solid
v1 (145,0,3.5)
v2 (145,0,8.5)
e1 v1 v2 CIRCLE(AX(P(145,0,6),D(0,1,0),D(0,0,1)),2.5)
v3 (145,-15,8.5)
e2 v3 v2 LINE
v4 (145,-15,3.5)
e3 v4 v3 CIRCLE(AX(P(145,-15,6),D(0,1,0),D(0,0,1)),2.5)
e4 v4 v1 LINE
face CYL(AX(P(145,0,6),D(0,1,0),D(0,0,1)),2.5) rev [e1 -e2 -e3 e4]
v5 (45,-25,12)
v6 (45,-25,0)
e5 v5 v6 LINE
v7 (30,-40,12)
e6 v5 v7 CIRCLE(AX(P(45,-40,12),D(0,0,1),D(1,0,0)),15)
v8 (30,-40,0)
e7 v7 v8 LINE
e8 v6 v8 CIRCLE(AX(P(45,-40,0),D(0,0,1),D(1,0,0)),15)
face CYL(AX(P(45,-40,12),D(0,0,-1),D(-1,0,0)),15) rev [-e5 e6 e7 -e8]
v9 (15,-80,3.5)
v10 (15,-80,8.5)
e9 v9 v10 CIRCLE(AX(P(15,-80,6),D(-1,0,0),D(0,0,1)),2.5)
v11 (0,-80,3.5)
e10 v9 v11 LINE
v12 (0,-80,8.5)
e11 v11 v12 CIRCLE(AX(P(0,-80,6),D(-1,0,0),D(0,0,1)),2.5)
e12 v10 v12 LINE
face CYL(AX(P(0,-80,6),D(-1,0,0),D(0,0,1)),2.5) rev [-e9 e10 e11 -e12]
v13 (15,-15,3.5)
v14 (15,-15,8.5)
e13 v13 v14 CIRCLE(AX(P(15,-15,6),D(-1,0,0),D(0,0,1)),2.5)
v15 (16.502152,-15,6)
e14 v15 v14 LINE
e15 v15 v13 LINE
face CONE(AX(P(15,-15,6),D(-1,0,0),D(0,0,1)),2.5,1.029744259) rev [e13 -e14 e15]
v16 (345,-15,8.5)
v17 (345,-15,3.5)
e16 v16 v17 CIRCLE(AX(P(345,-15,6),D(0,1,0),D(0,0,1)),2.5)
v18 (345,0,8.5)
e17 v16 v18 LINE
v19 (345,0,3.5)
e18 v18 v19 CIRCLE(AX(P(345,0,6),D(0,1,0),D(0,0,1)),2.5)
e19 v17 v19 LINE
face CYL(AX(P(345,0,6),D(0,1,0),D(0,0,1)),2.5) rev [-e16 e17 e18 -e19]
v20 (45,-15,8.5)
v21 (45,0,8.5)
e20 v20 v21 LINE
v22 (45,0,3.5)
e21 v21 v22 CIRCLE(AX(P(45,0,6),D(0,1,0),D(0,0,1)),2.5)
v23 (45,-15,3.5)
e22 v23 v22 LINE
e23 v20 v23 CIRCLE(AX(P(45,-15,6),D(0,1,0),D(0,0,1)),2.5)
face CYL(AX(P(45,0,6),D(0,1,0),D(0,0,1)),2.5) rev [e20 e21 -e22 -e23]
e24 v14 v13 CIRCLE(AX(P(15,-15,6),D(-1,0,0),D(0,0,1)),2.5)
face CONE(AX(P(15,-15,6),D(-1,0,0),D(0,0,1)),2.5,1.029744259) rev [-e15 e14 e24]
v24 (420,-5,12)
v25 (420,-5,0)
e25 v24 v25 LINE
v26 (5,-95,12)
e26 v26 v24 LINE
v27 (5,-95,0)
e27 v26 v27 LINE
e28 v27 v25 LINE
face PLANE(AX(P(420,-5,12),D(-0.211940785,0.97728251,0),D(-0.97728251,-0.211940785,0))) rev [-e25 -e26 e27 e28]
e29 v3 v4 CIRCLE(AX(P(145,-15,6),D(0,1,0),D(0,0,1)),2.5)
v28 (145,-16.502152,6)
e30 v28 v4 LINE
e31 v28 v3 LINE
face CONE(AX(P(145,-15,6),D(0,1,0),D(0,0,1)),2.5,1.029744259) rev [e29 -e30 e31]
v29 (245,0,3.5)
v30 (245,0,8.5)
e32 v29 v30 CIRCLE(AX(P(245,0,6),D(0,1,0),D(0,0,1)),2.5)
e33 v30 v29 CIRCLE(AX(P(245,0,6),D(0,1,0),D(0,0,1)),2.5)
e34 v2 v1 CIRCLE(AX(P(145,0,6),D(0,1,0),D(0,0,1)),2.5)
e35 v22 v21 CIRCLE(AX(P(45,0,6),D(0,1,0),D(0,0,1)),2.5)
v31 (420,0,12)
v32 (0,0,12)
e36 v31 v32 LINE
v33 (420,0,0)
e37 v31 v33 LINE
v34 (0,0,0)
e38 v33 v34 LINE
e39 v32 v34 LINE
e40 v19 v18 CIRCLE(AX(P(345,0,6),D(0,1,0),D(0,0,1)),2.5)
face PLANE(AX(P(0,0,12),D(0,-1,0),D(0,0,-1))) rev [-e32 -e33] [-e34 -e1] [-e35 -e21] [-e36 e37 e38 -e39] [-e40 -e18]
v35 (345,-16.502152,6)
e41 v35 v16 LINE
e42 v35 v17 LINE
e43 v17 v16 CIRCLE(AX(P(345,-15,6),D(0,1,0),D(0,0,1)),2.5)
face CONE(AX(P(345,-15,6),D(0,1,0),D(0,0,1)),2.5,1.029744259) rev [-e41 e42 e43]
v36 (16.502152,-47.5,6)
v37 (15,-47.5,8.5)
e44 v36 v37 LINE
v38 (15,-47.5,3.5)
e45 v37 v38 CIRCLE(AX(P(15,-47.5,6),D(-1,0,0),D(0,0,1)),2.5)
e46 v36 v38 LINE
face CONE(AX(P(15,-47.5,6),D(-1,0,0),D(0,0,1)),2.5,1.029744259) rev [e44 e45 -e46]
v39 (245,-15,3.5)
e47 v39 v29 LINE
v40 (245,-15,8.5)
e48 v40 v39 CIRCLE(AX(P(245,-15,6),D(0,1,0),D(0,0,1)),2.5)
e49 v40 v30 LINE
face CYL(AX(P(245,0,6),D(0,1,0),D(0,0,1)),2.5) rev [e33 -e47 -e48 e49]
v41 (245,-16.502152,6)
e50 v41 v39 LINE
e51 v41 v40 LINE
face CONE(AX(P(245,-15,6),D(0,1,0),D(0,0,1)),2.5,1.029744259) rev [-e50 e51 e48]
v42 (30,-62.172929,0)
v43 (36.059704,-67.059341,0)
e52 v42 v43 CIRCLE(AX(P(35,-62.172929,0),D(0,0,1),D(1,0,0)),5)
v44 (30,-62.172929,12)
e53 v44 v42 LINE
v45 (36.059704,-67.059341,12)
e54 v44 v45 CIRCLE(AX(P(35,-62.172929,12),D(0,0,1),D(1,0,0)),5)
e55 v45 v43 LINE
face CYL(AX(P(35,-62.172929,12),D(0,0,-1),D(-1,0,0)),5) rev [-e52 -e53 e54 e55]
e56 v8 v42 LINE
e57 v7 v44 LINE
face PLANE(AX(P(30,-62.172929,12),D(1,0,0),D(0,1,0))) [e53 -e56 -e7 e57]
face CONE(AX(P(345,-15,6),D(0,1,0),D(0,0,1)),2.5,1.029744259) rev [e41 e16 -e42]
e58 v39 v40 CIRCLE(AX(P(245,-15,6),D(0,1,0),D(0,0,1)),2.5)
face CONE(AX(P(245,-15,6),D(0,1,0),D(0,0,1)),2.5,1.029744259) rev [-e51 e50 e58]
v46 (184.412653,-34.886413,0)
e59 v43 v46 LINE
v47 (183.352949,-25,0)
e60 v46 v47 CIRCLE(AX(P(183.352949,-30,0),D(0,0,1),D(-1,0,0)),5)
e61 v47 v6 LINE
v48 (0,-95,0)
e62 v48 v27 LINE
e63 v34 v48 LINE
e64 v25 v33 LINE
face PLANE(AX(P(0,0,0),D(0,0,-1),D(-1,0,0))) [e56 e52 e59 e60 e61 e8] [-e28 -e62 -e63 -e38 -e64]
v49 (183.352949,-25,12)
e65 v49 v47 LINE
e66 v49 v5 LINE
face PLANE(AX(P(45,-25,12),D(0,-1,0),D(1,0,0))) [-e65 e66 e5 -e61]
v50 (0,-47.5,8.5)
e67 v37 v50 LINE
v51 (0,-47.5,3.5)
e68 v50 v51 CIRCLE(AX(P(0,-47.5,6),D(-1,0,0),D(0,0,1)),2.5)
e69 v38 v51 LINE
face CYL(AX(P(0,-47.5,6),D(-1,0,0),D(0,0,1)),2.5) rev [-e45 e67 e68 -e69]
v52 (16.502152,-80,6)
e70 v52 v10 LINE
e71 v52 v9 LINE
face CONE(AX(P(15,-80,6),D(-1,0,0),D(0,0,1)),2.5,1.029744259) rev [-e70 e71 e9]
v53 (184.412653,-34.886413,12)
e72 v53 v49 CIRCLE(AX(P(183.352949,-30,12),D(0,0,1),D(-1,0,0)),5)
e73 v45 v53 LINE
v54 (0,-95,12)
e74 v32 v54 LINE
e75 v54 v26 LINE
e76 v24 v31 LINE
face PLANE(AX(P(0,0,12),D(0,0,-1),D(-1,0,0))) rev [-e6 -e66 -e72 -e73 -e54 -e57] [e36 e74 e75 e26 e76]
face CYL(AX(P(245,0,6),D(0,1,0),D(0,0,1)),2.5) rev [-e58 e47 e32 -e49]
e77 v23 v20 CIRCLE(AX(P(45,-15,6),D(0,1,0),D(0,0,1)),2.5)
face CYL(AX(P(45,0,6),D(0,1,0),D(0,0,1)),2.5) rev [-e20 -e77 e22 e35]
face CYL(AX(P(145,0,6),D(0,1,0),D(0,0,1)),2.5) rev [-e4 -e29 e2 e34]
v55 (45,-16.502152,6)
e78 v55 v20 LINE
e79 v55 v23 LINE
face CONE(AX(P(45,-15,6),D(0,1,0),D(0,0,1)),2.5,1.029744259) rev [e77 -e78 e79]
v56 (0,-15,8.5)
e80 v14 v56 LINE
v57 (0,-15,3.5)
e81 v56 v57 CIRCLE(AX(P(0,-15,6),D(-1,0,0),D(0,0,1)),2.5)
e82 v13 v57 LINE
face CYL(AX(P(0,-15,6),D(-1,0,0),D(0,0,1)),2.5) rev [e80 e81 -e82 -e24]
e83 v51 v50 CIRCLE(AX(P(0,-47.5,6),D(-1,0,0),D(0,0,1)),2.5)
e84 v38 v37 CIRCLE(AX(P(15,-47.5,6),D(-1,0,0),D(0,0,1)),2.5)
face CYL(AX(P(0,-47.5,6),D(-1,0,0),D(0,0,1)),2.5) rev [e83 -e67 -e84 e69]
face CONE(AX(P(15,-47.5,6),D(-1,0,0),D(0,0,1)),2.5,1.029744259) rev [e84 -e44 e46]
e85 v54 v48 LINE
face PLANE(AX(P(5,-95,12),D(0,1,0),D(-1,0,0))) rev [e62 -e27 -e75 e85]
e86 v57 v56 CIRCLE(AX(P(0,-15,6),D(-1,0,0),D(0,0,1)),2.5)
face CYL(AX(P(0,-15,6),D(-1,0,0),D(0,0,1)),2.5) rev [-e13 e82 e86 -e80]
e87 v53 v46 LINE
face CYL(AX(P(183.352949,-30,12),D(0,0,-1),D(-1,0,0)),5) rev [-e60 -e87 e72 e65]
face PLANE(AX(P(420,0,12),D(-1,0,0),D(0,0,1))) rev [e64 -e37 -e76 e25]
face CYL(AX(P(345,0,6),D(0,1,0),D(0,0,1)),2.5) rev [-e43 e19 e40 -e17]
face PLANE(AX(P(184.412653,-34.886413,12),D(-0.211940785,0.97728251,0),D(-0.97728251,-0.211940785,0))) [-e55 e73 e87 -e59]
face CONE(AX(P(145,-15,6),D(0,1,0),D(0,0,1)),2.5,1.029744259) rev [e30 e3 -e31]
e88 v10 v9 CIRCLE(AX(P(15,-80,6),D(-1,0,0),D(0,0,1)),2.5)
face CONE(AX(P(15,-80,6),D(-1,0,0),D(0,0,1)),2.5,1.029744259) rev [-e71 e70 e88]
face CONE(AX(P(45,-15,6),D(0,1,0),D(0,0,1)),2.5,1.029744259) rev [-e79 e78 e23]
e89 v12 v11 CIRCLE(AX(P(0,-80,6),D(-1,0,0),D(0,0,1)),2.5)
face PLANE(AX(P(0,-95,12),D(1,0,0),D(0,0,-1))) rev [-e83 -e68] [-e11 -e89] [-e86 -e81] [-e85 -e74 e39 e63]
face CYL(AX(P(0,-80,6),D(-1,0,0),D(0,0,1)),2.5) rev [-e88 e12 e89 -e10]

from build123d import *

# Parameters (mm, degrees)
BOSS_EXTRUDE1_DEPTH   = 12
M6_TAPPED_HOLE1_D     = 5
M6_TAPPED_HOLE1_DEPTH = 15
M6_TAPPED_HOLE1_TIP   = 1.502151548
M6_TAPPED_HOLE2_D     = 5
M6_TAPPED_HOLE2_DEPTH = 15
M6_TAPPED_HOLE2_TIP   = 1.502151548


with BuildPart() as part:
    # Sketch1 → Boss-Extrude1 (new body)
    with BuildSketch(Plane.XY):
        Polygon((0, -95), (0, 0), (420, 0), (420, -5), (5, -95), align=None)
        with BuildLine():
            Line((30, -62.172928769), (30, -40))
            ThreePointArc((30, -40), (34.393398282, -29.393398282), (45, -25))
            Line((45, -25), (183.352949325, -25))
            ThreePointArc((183.352949325, -25), (188.324471362, -29.467112929), (184.412653251, -34.886412548))
            Line((184.412653251, -34.886412548), (36.059703926, -67.059341317))
            ThreePointArc((36.059703926, -67.059341317), (31.861411116, -66.065133776), (30, -62.172928769))
        make_face(mode=Mode.SUBTRACT)
    extrude(amount=BOSS_EXTRUDE1_DEPTH)

    # M6 Tapped Hole1
    with Locations(Plane.ZY):
        with Locations((6, -15), (6, -47.5), (6, -80)):
            Hole(M6_TAPPED_HOLE1_D / 2, depth=M6_TAPPED_HOLE1_DEPTH)
            with Locations((0, 0, -(M6_TAPPED_HOLE1_DEPTH + M6_TAPPED_HOLE1_TIP / 2))):  # 118° drill point
                Cone(0, M6_TAPPED_HOLE1_D / 2, M6_TAPPED_HOLE1_TIP, mode=Mode.SUBTRACT)

    # M6 Tapped Hole2
    with Locations(Plane(origin=(0, 0, 0), x_dir=(-1, 0, 0), z_dir=(0, 1, 0))):
        with Locations((-45, 6), (-145, 6), (-245, 6), (-345, 6)):
            Hole(M6_TAPPED_HOLE2_D / 2, depth=M6_TAPPED_HOLE2_DEPTH)
            with Locations((0, 0, -(M6_TAPPED_HOLE2_DEPTH + M6_TAPPED_HOLE2_TIP / 2))):  # 118° drill point
                Cone(0, M6_TAPPED_HOLE2_D / 2, M6_TAPPED_HOLE2_TIP, mode=Mode.SUBTRACT)


solid = part.part
